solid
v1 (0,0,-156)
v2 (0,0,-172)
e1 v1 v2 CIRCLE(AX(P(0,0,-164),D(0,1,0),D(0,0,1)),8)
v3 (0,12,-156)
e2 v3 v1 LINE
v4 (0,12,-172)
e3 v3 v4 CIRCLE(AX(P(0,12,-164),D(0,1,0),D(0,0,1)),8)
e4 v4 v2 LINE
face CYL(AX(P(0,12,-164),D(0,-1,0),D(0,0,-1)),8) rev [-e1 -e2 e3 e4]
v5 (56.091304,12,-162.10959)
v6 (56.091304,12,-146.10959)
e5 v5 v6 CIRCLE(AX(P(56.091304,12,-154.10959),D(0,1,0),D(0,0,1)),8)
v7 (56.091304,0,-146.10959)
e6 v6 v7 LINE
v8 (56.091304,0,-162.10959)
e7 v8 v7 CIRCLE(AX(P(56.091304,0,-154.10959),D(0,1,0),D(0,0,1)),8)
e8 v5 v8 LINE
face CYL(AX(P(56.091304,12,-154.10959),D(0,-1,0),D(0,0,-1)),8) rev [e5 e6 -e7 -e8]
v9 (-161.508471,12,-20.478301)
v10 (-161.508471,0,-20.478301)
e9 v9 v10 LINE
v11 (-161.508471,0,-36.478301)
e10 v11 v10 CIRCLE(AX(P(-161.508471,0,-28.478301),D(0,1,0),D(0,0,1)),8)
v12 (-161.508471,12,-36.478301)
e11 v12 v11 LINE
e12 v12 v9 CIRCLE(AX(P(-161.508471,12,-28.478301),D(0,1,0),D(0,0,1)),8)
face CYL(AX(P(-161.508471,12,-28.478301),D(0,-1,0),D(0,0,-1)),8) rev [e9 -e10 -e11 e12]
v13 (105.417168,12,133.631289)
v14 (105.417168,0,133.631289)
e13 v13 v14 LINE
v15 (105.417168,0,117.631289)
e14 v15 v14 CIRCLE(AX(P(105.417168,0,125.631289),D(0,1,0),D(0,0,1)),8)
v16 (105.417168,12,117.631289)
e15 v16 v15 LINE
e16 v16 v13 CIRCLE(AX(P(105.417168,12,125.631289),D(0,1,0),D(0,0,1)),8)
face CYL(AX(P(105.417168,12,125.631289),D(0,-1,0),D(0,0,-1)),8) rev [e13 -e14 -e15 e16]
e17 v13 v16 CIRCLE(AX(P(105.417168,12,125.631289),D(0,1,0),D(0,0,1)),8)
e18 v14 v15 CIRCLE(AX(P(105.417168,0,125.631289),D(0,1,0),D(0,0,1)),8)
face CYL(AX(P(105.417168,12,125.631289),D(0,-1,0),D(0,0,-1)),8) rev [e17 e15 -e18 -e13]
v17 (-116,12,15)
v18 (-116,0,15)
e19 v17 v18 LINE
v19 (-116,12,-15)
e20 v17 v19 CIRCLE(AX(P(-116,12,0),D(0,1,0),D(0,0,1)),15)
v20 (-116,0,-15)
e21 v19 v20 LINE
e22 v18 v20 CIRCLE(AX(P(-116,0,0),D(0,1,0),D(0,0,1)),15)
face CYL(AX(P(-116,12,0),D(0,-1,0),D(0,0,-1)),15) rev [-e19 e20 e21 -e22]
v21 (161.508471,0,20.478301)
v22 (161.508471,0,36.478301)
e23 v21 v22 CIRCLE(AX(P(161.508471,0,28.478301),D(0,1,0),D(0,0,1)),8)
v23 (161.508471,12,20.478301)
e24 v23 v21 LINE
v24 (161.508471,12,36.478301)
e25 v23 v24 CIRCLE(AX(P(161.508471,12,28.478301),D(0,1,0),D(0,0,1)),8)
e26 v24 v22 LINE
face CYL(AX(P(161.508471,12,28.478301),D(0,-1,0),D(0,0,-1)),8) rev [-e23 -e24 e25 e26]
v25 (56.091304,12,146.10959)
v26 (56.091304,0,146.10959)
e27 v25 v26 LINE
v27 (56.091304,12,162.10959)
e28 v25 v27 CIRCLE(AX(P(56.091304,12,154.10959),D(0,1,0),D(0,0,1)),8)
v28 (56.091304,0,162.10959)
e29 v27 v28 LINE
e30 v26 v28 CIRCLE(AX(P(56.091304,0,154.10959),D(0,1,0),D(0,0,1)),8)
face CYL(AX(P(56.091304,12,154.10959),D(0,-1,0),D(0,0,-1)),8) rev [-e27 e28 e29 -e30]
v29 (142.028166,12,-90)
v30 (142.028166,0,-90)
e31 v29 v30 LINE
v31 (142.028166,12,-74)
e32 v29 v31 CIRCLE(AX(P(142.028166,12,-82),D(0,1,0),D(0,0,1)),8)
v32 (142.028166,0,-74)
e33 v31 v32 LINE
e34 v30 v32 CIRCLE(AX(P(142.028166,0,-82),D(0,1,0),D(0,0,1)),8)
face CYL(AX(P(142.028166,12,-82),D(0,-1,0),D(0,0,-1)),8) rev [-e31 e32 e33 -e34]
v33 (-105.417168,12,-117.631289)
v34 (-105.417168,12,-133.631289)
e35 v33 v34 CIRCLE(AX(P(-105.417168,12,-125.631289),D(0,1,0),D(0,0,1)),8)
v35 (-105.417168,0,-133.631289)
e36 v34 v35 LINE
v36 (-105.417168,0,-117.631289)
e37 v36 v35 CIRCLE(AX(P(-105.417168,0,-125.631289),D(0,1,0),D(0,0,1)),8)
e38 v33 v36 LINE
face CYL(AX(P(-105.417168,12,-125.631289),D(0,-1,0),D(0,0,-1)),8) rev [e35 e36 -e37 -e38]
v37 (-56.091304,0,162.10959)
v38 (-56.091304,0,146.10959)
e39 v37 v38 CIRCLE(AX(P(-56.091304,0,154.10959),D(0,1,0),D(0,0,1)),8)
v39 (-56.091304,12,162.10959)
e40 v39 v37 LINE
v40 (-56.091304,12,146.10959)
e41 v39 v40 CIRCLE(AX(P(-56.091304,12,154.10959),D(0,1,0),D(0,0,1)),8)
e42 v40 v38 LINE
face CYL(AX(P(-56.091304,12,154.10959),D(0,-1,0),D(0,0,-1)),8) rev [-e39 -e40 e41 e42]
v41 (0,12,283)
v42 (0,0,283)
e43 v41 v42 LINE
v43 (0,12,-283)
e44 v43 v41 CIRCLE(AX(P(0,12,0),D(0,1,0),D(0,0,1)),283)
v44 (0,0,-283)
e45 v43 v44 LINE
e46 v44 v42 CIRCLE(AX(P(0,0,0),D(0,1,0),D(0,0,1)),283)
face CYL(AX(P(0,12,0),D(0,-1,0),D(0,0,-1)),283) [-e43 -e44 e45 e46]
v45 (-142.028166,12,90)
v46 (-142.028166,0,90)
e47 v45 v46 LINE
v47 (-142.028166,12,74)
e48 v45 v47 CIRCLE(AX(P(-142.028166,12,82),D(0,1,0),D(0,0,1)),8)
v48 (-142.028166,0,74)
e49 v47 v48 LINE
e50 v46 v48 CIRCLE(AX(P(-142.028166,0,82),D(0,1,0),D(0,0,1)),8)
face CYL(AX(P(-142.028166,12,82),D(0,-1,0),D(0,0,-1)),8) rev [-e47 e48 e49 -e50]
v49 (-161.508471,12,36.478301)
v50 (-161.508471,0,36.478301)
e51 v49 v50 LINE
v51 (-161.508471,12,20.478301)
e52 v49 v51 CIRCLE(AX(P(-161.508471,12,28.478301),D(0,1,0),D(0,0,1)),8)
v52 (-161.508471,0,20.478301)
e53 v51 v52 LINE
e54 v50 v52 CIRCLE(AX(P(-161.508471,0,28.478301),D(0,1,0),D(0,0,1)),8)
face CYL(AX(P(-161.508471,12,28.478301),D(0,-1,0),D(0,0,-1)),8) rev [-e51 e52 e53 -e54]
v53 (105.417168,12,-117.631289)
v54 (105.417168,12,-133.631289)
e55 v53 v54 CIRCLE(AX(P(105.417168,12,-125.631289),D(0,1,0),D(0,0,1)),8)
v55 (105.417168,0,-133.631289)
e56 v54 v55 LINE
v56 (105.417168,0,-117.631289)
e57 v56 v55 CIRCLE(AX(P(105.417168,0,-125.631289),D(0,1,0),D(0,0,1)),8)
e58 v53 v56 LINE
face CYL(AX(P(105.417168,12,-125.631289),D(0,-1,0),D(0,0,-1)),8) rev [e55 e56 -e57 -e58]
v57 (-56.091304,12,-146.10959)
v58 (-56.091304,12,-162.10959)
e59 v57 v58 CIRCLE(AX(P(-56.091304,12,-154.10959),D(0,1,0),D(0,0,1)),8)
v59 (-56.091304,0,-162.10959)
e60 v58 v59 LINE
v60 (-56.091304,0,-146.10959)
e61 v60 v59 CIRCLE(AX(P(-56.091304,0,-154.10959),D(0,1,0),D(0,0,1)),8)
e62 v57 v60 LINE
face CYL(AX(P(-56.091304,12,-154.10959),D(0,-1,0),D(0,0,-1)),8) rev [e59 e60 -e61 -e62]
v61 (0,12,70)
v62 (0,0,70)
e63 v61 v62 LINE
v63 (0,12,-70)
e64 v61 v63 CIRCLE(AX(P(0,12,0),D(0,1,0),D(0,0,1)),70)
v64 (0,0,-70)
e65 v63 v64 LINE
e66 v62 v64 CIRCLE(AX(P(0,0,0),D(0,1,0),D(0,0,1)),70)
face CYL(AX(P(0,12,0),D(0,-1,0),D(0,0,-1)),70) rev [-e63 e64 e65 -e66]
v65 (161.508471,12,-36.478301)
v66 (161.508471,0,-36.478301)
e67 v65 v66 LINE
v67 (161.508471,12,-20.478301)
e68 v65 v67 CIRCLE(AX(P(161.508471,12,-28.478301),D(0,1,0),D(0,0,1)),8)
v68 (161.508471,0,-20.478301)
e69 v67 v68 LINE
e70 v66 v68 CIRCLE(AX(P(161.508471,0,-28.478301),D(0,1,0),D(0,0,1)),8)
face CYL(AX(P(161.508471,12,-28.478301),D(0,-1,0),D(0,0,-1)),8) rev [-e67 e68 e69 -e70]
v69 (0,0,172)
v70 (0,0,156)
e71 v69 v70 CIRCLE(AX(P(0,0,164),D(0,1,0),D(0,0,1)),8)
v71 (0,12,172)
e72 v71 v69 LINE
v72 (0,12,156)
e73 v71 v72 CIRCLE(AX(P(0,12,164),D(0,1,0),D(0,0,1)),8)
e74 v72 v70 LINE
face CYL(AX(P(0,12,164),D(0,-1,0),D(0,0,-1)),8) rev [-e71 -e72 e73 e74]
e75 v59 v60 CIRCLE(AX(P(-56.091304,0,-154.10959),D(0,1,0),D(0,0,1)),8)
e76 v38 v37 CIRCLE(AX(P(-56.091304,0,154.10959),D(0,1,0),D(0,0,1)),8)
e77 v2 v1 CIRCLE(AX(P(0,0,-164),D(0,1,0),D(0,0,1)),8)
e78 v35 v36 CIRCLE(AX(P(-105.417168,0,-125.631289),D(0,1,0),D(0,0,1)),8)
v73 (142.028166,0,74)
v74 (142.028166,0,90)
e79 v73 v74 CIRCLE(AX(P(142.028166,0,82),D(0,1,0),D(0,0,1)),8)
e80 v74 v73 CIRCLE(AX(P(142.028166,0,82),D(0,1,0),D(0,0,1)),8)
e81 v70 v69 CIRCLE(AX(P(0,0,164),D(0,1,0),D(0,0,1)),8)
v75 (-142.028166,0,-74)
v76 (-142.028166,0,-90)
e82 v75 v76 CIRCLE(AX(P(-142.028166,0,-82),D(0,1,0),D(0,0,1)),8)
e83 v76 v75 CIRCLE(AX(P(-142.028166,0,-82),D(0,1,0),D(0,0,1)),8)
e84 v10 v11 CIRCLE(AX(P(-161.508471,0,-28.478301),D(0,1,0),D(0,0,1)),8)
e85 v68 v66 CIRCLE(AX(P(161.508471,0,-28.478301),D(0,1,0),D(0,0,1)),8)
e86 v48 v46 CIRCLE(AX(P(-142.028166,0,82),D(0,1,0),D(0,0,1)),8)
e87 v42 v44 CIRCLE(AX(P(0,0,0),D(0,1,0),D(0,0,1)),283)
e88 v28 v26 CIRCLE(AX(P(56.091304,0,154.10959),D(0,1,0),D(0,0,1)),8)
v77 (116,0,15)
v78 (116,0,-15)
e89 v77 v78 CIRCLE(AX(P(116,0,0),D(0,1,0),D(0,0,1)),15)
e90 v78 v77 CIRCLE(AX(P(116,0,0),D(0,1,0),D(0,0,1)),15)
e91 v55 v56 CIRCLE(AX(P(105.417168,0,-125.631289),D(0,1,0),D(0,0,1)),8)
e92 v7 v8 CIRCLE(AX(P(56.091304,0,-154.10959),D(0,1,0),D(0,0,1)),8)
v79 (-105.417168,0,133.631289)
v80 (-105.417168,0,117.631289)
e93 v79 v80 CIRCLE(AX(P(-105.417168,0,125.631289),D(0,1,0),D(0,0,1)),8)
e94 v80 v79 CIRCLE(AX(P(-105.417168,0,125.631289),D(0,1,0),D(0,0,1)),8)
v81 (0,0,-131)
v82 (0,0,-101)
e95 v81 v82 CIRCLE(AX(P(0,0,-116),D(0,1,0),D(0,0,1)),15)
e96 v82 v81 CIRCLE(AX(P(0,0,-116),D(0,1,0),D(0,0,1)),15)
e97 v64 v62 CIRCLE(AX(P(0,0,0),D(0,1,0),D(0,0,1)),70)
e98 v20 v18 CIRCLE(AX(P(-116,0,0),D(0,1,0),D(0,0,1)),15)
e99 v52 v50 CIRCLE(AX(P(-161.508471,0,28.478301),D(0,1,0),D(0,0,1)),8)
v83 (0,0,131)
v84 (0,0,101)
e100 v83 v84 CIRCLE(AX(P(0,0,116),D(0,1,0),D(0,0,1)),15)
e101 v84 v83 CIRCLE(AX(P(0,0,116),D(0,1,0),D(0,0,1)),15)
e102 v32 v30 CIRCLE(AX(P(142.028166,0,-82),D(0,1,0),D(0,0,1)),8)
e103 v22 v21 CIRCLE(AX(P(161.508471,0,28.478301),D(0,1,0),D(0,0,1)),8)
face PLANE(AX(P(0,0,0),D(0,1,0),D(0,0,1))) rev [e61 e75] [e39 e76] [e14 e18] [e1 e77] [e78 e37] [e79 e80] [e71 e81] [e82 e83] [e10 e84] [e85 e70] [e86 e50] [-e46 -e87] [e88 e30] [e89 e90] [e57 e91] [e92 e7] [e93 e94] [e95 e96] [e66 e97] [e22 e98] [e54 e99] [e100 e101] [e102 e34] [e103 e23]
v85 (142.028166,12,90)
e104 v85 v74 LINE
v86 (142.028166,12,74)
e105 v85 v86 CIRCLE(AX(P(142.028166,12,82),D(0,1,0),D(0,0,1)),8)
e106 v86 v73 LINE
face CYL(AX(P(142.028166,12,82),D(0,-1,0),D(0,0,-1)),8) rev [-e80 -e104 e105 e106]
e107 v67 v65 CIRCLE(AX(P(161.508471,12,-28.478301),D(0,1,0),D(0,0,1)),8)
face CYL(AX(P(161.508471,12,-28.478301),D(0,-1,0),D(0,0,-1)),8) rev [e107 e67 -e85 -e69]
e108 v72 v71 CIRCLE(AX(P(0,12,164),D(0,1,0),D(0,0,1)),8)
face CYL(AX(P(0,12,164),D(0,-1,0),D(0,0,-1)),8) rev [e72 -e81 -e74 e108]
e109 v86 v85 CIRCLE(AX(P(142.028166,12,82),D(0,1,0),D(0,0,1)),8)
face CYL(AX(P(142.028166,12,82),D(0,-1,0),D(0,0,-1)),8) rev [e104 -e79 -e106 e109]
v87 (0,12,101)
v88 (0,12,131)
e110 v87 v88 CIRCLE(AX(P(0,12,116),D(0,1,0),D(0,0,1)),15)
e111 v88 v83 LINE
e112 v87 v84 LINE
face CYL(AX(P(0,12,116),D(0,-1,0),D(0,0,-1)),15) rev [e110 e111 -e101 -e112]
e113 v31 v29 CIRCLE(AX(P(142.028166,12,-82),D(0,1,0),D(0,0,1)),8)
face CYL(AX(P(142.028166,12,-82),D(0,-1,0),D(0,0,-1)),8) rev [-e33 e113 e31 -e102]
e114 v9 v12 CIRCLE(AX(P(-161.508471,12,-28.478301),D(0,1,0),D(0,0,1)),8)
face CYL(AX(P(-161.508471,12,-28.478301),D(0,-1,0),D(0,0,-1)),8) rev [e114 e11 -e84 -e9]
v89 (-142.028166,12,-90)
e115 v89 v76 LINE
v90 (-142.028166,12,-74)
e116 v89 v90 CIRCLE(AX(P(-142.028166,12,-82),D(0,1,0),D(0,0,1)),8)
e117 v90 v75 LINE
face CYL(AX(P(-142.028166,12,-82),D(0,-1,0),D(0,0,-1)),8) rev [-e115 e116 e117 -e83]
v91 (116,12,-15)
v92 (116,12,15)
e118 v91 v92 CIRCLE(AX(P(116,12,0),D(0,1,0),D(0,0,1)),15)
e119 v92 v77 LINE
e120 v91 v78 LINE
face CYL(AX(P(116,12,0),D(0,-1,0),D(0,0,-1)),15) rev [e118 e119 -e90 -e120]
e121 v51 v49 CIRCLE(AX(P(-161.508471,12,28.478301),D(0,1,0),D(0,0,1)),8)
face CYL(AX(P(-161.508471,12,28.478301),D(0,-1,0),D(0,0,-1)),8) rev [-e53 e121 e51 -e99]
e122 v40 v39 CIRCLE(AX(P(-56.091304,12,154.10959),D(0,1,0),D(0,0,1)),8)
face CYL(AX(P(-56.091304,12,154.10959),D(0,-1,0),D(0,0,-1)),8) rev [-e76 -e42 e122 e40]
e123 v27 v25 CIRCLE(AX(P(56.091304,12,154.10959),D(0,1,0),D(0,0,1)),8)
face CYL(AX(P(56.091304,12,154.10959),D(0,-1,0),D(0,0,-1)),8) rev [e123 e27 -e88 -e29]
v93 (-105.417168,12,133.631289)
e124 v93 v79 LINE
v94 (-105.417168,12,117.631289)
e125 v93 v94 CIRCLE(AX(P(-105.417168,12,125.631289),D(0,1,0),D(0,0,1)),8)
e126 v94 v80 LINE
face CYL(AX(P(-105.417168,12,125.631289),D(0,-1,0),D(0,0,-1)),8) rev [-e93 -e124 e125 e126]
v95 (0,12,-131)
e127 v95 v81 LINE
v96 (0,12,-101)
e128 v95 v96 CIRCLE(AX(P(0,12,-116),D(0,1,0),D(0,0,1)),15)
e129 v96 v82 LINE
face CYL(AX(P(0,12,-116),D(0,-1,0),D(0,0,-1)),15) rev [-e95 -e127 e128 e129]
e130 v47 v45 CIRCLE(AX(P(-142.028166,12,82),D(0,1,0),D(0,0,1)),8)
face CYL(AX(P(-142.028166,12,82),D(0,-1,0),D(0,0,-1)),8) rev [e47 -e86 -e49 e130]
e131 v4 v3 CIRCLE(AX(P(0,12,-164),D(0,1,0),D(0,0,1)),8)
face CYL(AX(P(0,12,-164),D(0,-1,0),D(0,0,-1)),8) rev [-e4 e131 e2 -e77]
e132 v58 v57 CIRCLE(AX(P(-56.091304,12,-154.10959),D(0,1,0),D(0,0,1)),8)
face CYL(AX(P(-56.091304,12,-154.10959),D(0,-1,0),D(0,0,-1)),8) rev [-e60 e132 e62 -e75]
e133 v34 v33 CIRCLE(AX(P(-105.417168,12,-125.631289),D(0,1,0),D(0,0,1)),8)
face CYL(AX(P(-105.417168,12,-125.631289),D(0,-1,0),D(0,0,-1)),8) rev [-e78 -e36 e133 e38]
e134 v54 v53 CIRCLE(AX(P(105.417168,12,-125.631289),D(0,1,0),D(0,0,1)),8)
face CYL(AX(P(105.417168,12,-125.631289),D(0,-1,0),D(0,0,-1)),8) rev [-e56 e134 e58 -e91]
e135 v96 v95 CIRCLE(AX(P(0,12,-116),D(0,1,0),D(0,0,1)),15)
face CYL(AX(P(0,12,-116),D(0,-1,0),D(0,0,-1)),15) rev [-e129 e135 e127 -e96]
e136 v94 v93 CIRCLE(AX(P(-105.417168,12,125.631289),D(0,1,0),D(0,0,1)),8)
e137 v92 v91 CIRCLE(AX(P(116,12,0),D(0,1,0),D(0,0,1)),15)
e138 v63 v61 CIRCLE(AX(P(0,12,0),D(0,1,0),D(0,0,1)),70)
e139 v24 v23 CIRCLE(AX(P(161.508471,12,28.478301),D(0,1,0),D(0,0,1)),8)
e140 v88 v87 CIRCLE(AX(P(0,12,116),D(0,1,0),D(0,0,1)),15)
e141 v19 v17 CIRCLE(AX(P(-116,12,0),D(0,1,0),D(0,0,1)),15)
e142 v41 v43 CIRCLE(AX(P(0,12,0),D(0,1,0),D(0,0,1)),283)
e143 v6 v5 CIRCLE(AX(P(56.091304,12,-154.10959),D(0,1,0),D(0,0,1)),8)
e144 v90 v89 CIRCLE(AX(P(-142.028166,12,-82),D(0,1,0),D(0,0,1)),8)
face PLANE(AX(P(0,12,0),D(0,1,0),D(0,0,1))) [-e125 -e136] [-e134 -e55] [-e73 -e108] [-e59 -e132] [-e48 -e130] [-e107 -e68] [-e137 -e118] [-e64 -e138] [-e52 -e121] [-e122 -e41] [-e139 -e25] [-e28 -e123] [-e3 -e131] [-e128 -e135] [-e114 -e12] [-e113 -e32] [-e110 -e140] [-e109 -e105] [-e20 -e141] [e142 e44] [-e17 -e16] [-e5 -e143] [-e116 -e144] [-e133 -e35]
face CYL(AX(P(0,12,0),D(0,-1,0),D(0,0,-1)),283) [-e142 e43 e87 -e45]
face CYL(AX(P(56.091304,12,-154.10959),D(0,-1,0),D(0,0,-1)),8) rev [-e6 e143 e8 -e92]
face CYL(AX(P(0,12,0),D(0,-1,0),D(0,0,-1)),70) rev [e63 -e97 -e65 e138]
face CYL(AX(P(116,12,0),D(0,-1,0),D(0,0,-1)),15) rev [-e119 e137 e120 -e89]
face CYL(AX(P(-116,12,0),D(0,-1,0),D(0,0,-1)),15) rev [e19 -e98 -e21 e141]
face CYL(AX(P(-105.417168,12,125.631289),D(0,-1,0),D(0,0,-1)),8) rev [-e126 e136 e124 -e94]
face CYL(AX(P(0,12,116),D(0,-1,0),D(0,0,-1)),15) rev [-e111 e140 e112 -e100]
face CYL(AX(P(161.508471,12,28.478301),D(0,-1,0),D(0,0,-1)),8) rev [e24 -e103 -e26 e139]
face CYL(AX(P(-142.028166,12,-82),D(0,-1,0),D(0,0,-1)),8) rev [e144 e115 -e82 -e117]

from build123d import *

# Parameters (mm, degrees)
SKETCH1_R           = 283
SKETCH1_R_2         = 70
SKETCH1_R_3         = 15
SKETCH1_R_4         = 8
BOSS_EXTRUDE1_DEPTH = 12


with BuildPart() as part:
    # Sketch1 → Boss-Extrude1 (new body)
    with BuildSketch(Plane(origin=(0, 0, 0), x_dir=(1, 0, 0), z_dir=(0, 1, 0))):
        with Locations(Location((0, 0, 0), (0, 0, 270))):
            Circle(SKETCH1_R)
        with Locations(Location((0, 0, 0), (0, 0, 270))):
            Circle(SKETCH1_R_2, mode=Mode.SUBTRACT)
        with Locations(Location((0, 116, 0), (0, 0, 270))):
            Circle(SKETCH1_R_3, mode=Mode.SUBTRACT)
        with Locations(Location((0, 164, 0), (0, 0, 270))):
            Circle(SKETCH1_R_4, mode=Mode.SUBTRACT)
        with Locations(Location((56.091303505, 154.109589809, 0), (0, 0, 270))):
            Circle(SKETCH1_R_4, mode=Mode.SUBTRACT)
        with Locations(Location((105.417167989, 125.631288672, 0), (0, 0, 270))):
            Circle(SKETCH1_R_4, mode=Mode.SUBTRACT)
        with Locations(Location((142.028166221, 82, 0), (0, 0, 270))):
            Circle(SKETCH1_R_4, mode=Mode.SUBTRACT)
        with Locations(Location((161.508471494, 28.478301137, 0), (0, 0, 270))):
            Circle(SKETCH1_R_4, mode=Mode.SUBTRACT)
        with Locations(Location((161.508471494, -28.478301137, 0), (0, 0, 270))):
            Circle(SKETCH1_R_4, mode=Mode.SUBTRACT)
        with Locations(Location((142.028166221, -82, 0), (0, 0, 270))):
            Circle(SKETCH1_R_4, mode=Mode.SUBTRACT)
        with Locations(Location((105.417167989, -125.631288672, 0), (0, 0, 270))):
            Circle(SKETCH1_R_4, mode=Mode.SUBTRACT)
        with Locations(Location((56.091303505, -154.109589809, 0), (0, 0, 270))):
            Circle(SKETCH1_R_4, mode=Mode.SUBTRACT)
        with Locations(Location((0, -164, 0), (0, 0, 270))):
            Circle(SKETCH1_R_4, mode=Mode.SUBTRACT)
        with Locations(Location((-56.091303505, -154.109589809, 0), (0, 0, 270))):
            Circle(SKETCH1_R_4, mode=Mode.SUBTRACT)
        with Locations(Location((-105.417167989, -125.631288672, 0), (0, 0, 270))):
            Circle(SKETCH1_R_4, mode=Mode.SUBTRACT)
        with Locations(Location((-142.028166221, -82, 0), (0, 0, 270))):
            Circle(SKETCH1_R_4, mode=Mode.SUBTRACT)
        with Locations(Location((-161.508471494, -28.478301137, 0), (0, 0, 270))):
            Circle(SKETCH1_R_4, mode=Mode.SUBTRACT)
        with Locations(Location((-161.508471494, 28.478301137, 0), (0, 0, 270))):
            Circle(SKETCH1_R_4, mode=Mode.SUBTRACT)
        with Locations(Location((-142.028166221, 82, 0), (0, 0, 270))):
            Circle(SKETCH1_R_4, mode=Mode.SUBTRACT)
        with Locations(Location((-105.417167989, 125.631288672, 0), (0, 0, 270))):
            Circle(SKETCH1_R_4, mode=Mode.SUBTRACT)
        with Locations(Location((-56.091303505, 154.109589809, 0), (0, 0, 270))):
            Circle(SKETCH1_R_4, mode=Mode.SUBTRACT)
        with Locations(Location((116, 0, 0), (0, 0, 270))):
            Circle(SKETCH1_R_3, mode=Mode.SUBTRACT)
        with Locations(Location((0, -116, 0), (0, 0, 270))):
            Circle(SKETCH1_R_3, mode=Mode.SUBTRACT)
        with Locations(Location((-116, 0, 0), (0, 0, 270))):
            Circle(SKETCH1_R_3, mode=Mode.SUBTRACT)
    extrude(amount=BOSS_EXTRUDE1_DEPTH)


solid = part.part
